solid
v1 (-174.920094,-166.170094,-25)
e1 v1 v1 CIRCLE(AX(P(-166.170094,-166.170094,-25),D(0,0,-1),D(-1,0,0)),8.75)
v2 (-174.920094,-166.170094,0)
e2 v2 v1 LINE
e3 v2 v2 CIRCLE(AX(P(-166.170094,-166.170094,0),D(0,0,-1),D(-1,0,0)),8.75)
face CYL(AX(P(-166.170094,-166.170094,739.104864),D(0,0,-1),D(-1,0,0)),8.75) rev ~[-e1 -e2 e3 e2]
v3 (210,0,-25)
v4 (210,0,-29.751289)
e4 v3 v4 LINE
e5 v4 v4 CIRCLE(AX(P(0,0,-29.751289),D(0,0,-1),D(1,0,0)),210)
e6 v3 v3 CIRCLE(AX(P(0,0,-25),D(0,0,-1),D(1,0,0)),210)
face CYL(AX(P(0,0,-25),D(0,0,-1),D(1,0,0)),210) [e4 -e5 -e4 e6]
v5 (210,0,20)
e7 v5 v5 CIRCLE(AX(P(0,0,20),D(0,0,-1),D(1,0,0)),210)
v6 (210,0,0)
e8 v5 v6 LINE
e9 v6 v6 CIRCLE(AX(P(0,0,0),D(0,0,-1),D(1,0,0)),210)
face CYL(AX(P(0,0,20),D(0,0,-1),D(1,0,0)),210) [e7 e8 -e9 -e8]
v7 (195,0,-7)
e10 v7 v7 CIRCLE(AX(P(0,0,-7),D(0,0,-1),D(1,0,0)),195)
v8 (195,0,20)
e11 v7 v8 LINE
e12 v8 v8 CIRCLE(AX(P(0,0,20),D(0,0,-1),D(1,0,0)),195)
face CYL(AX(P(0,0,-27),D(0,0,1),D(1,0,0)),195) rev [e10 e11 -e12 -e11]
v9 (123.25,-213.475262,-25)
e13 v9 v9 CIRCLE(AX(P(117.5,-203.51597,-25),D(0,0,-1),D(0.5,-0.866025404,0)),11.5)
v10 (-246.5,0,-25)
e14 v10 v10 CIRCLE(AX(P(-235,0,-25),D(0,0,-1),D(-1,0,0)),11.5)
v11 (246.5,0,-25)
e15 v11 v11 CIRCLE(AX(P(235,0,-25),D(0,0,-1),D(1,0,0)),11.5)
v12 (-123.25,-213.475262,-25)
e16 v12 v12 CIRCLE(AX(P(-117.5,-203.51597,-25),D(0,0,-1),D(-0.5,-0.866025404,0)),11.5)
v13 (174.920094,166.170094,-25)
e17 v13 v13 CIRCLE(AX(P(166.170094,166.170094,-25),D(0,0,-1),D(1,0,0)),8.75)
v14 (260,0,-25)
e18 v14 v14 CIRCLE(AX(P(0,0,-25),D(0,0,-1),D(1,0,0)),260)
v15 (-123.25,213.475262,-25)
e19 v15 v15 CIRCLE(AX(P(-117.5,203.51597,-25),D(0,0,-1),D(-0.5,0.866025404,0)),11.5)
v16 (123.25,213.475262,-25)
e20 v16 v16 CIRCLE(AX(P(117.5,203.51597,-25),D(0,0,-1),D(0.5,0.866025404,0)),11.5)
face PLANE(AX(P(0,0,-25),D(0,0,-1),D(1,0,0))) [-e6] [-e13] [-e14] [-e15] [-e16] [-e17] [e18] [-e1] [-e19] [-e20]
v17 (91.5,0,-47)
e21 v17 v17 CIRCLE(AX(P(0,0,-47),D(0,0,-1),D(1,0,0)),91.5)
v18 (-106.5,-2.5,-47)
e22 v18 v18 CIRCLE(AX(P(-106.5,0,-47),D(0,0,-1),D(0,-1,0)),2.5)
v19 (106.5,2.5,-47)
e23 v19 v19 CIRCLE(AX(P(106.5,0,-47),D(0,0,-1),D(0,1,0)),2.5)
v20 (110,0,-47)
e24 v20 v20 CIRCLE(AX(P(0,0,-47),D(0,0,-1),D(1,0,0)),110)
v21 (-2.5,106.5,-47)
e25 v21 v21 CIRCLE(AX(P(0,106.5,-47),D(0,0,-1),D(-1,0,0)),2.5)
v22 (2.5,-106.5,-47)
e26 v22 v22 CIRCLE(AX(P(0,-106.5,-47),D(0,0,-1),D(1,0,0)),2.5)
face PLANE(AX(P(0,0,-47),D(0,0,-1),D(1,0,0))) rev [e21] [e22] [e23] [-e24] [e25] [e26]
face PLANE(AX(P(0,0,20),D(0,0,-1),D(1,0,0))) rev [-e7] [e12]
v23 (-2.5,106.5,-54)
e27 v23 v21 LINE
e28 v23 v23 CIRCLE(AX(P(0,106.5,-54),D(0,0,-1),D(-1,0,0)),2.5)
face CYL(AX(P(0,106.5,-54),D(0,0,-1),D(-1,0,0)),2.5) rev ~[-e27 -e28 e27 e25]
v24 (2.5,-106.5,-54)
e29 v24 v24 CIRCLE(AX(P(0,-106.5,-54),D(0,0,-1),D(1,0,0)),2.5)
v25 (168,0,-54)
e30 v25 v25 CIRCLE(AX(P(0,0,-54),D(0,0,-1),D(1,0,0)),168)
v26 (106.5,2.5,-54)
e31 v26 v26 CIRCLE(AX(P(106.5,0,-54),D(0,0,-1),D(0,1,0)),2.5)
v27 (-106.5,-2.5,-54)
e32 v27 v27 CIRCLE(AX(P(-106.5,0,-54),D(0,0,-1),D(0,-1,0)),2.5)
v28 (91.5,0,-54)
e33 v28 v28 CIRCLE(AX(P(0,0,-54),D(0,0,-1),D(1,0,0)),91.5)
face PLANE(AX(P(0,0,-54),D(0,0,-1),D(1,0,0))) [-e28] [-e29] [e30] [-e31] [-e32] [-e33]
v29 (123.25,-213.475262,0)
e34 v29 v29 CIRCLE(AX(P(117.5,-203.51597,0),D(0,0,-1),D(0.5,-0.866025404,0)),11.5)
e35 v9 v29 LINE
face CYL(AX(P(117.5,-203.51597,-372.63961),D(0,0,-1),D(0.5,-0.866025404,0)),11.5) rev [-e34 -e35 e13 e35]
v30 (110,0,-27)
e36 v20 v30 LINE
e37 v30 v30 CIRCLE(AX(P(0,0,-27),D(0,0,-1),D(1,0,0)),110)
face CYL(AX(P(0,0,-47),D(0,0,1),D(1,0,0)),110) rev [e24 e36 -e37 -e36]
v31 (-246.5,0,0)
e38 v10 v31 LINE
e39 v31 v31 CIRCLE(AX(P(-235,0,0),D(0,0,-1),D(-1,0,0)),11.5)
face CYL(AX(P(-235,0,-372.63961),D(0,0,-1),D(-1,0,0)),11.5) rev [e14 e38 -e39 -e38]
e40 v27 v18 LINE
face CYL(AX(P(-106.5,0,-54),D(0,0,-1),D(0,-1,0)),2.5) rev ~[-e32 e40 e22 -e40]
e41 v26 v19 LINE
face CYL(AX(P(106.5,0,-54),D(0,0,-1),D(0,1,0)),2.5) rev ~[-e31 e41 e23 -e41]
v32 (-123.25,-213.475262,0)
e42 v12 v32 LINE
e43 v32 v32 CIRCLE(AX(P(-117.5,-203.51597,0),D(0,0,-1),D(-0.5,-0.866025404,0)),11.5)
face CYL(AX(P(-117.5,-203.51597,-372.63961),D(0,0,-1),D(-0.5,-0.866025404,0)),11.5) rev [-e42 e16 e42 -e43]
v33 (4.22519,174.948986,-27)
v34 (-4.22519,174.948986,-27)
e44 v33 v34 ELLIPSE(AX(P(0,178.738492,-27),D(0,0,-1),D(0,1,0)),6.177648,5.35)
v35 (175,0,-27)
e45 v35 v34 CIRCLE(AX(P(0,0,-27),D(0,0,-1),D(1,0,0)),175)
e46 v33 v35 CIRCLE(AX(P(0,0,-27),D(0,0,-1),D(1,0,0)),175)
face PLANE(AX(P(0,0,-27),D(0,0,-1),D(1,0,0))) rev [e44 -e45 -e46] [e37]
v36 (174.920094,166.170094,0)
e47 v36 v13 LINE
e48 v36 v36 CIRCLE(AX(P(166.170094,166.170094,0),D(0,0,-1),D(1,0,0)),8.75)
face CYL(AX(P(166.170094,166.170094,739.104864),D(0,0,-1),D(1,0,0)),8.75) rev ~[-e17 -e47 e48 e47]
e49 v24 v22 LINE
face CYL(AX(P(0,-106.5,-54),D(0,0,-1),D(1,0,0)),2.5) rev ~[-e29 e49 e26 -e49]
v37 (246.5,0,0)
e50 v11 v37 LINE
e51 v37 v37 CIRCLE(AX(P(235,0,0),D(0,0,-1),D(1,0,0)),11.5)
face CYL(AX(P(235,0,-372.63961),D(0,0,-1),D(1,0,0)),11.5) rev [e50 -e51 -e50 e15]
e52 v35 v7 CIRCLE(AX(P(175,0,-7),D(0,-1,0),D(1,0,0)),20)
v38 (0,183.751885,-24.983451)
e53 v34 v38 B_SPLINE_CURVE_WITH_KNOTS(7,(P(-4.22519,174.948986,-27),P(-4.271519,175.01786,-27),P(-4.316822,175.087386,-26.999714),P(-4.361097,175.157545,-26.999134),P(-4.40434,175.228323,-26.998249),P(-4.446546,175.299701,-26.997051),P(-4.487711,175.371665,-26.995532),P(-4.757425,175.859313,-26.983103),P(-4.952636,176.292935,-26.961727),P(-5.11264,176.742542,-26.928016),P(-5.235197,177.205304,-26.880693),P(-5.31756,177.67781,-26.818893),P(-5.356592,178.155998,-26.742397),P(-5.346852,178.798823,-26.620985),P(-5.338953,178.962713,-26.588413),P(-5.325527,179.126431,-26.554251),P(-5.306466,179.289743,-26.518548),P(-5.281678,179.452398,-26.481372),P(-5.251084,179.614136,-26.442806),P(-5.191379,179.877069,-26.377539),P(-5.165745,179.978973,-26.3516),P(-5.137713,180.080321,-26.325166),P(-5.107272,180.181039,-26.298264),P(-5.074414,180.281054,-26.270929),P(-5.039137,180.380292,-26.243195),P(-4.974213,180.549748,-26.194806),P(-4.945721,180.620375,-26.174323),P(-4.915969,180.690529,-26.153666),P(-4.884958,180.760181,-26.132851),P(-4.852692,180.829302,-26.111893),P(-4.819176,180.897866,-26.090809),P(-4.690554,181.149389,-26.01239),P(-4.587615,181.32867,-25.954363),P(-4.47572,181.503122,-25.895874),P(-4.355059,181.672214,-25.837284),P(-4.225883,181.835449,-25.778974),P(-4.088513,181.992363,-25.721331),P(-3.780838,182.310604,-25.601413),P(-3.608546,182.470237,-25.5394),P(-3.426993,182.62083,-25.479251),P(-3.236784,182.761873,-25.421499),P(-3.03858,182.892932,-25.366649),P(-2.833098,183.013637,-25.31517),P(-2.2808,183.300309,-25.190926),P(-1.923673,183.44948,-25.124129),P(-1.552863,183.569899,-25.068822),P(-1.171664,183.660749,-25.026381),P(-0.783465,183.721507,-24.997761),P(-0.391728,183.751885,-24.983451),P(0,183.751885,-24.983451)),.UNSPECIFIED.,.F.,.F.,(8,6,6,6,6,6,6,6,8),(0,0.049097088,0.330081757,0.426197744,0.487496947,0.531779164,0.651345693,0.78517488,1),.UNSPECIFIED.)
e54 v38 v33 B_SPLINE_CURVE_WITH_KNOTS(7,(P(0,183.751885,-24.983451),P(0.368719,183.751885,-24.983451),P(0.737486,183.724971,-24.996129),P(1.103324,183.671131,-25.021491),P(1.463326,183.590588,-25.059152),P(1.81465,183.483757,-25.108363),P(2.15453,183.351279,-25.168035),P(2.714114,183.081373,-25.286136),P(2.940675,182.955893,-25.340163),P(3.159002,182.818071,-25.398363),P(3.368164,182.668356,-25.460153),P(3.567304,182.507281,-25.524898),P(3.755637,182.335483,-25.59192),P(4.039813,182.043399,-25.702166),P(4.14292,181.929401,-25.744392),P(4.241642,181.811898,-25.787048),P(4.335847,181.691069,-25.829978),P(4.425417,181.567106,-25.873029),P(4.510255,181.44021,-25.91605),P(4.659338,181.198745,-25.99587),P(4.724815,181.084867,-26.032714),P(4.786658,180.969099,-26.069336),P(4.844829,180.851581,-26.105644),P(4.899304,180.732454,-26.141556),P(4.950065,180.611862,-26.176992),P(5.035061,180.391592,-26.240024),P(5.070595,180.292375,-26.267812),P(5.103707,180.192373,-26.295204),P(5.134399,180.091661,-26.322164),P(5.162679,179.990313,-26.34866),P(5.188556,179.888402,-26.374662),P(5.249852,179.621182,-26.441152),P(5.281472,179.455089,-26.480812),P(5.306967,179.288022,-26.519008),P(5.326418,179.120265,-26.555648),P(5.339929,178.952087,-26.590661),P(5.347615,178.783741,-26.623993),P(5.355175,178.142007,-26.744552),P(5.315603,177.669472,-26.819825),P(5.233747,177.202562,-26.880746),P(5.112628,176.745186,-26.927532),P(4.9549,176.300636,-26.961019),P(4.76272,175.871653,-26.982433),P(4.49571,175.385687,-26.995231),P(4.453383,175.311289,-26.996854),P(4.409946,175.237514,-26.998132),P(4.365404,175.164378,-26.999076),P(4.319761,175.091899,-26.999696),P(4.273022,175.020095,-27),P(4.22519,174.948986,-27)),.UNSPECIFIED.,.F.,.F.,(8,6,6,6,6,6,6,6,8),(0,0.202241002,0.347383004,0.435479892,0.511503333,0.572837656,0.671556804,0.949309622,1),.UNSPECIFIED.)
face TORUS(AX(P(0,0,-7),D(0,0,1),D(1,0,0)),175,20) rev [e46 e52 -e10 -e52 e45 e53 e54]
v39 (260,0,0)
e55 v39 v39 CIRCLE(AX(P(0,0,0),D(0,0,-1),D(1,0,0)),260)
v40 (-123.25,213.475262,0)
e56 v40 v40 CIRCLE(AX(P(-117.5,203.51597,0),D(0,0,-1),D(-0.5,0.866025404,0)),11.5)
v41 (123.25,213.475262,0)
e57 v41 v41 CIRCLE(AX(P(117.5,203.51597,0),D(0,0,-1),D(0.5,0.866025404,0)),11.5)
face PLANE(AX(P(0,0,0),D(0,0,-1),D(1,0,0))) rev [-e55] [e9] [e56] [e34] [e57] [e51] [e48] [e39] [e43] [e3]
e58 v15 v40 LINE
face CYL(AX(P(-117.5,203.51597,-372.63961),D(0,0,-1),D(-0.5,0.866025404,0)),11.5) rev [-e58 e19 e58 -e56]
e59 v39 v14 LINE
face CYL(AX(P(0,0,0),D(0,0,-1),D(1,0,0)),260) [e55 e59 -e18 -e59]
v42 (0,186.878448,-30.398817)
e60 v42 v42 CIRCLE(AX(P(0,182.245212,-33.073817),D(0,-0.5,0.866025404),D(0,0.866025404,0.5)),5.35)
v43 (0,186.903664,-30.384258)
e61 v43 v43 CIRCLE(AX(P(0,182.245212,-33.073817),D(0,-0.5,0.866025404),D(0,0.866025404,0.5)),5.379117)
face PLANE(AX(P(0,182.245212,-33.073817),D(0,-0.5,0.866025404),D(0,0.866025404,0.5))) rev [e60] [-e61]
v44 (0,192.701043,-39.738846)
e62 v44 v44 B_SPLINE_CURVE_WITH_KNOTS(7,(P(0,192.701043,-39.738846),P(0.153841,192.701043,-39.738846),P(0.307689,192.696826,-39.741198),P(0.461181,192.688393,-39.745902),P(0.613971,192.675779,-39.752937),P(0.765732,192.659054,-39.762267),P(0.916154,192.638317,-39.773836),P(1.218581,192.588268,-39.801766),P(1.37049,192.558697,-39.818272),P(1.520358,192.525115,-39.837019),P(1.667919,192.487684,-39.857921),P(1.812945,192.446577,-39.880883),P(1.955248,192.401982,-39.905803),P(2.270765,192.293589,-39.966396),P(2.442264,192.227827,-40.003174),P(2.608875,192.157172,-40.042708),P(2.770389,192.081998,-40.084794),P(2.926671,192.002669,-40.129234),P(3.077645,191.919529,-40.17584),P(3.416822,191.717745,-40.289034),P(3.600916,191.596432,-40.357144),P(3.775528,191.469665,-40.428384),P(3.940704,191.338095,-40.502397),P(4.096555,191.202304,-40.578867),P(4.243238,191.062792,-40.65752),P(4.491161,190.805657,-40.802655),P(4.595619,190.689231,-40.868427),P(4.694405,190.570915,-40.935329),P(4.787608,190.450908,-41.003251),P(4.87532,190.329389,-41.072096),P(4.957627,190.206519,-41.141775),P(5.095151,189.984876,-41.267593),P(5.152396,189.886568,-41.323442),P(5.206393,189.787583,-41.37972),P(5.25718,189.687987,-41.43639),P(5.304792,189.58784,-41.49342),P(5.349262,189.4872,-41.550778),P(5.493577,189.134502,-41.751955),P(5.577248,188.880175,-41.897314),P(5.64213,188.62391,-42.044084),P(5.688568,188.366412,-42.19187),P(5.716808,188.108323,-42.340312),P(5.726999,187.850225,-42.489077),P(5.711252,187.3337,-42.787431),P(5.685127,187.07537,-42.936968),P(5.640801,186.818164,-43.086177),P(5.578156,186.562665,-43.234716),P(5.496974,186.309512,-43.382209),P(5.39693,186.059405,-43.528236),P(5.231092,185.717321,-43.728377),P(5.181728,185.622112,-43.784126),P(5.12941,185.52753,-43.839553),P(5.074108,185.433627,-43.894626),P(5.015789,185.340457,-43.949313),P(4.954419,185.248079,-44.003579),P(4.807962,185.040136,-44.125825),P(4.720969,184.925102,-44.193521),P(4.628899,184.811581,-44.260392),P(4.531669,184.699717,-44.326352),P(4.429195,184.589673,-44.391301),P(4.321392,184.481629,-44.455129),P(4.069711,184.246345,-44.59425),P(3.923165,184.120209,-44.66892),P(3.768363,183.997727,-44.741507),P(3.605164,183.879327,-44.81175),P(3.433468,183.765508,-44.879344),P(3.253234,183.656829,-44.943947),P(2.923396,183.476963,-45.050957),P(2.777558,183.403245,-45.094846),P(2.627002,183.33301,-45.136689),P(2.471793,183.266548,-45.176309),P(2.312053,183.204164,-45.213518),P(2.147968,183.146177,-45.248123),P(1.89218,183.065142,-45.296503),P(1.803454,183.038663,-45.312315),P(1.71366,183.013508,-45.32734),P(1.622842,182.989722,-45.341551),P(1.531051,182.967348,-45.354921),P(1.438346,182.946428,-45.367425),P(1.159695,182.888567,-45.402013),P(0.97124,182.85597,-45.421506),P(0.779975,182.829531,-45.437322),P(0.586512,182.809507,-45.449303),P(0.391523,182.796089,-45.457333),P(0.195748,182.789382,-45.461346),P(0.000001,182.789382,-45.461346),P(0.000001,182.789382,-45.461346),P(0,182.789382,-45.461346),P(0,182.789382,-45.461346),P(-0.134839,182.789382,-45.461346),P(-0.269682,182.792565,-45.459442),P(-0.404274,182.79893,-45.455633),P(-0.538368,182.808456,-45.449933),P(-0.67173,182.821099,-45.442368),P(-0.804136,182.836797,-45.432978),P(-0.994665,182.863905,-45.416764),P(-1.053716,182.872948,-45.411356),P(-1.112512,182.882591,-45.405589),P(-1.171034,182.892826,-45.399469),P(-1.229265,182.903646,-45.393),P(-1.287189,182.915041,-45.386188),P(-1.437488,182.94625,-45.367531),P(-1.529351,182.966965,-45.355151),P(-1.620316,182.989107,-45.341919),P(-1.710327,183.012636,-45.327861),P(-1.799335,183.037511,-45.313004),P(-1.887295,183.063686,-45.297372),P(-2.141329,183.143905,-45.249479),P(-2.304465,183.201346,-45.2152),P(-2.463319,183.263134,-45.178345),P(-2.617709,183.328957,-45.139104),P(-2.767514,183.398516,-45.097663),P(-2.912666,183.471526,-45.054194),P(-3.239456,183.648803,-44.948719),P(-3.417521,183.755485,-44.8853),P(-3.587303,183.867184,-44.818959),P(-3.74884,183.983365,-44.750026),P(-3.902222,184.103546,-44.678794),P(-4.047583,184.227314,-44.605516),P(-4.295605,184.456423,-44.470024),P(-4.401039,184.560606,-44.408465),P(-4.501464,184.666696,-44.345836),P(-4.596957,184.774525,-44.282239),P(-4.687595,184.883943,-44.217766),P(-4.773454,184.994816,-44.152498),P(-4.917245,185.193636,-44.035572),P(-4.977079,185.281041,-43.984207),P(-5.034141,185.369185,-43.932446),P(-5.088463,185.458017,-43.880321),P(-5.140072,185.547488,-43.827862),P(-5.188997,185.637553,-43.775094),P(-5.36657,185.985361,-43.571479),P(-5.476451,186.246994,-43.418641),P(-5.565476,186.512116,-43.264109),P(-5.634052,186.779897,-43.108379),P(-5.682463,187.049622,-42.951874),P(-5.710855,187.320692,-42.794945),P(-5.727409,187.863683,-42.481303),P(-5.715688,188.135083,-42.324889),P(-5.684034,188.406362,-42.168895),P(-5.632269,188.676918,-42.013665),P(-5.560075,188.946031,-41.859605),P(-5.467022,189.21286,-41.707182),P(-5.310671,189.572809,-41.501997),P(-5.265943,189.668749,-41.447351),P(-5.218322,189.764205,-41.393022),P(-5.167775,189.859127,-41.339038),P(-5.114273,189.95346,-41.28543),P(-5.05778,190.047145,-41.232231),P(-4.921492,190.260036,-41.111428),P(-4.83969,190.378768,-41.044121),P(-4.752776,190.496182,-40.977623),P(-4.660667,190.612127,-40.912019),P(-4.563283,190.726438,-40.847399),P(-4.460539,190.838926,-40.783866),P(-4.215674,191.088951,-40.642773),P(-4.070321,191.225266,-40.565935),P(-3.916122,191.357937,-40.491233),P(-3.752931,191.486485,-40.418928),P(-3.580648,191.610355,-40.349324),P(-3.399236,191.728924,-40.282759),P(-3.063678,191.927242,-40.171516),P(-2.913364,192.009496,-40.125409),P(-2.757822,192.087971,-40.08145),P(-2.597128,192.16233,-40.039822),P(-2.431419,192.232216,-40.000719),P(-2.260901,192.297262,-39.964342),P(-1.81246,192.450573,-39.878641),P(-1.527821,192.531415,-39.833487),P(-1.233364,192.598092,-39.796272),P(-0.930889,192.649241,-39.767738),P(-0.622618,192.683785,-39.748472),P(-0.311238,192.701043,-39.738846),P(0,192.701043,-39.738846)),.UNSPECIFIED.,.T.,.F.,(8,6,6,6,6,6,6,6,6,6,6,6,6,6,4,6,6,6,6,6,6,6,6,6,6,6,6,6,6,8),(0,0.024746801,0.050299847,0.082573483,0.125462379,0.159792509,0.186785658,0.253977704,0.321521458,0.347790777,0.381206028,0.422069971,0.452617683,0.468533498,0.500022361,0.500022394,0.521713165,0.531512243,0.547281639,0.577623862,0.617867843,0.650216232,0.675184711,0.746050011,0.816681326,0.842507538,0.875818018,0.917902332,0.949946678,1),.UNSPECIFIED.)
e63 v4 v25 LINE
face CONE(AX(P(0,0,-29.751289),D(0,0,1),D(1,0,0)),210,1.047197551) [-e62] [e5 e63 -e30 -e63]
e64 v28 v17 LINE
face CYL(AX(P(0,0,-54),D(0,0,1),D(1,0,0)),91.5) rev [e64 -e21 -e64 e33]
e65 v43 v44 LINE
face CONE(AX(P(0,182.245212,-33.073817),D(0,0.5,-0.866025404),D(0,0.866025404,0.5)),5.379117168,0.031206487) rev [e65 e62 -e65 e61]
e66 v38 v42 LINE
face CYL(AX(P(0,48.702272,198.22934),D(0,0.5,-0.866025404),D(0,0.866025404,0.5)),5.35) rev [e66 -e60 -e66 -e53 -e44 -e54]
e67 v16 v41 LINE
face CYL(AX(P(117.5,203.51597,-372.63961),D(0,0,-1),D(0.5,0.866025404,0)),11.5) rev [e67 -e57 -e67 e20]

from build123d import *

# Parameters (mm, degrees)
FILLET1_R          = 20
CUT_EXTRUDE1_REACH = 377.068
SKETCH2_R          = 2.5
CIRPATTERN1_COUNT  = 4
CUT_EXTRUDE2_START = -372.639610375
SKETCH3_R          = 11.5
CUT_EXTRUDE2_DEPTH = 377.639610375
CIRPATTERN2_COUNT  = 6
M20_TAPPED_HOLE1_D = 17.5
CIRPATTERN3_COUNT  = 2


with BuildPart() as part:
    # Sketch1 → Revolve1 (revolve)
    with BuildSketch(Plane(origin=(0, 0, 0), x_dir=(0, 0, -1), z_dir=(1, 0, 0)), mode=Mode.PRIVATE) as revolve1_sk:
        Polygon((0, 260), (25, 260), (25, 210), (29.751288694, 210), (54, 168), (54, 91.5), (47, 91.5), (47, 110), (27, 110), (27, 195), (-20, 195), (-20, 210), (0, 210), align=None)
    revolve(revolve1_sk.sketch.rotate(Axis((0, 0, 141.233138436), (0, 0, -1)), 90), axis=Axis((0, 0, 141.233138436), (0, 0, -1)))

    # Fillet1
    fillet1_edges = [part.edges().sort_by_distance(p)[0] for p in [
        (-195, 0, -27),
    ]]
    fillet(fillet1_edges, radius=FILLET1_R)

    # Sketch2 → Cut-Extrude1 (cut, up to next)
    with BuildSketch(Plane(origin=(0, 0, -54), x_dir=(-1, 0, 0), z_dir=(0, 0, -1)), mode=Mode.PRIVATE) as cut_extrude1_sk1:
        with Locations((0, 106.5)):
            Circle(SKETCH2_R)
    cut_extrude1_tool1 = extrude(cut_extrude1_sk1.sketch, amount=-CUT_EXTRUDE1_REACH, mode=Mode.PRIVATE) & part.part
    cut_extrude1 = cut_extrude1_tool1.solids().sort_by_distance((0, 106.5, -54))[0]
    add(cut_extrude1, mode=Mode.SUBTRACT)

    # CirPattern1: Cut-Extrude1 ×4 about axis
    cirpattern1_axis = Axis((0, 0, 0), (0, 0, 1))
    for i in range(1, CIRPATTERN1_COUNT):
        add(cut_extrude1.rotate(cirpattern1_axis, i * 360 / CIRPATTERN1_COUNT), mode=Mode.SUBTRACT)

    # Sketch3 → Cut-Extrude2 (cut)
    with BuildSketch(Plane.XY.offset(CUT_EXTRUDE2_START)):
        with Locations(Location((-235, 0, 0), (0, 0, 180))):
            Circle(SKETCH3_R)
    cut_extrude2 = extrude(amount=CUT_EXTRUDE2_DEPTH, mode=Mode.SUBTRACT)

    # CirPattern2: Cut-Extrude2 ×6 about axis
    cirpattern2_axis = Axis((0, 0, 0), (0, 0, 1))
    for i in range(1, CIRPATTERN2_COUNT):
        add(cut_extrude2.rotate(cirpattern2_axis, i * 360 / CIRPATTERN2_COUNT), mode=Mode.SUBTRACT)

    # M20 Tapped Hole1 (through all)
    with Locations(Plane.XY):
        with Locations((-166.170093579, -166.170093579)):
            m20_tapped_hole1 = Hole(M20_TAPPED_HOLE1_D / 2)

    # CirPattern3: M20 Tapped Hole1 ×2 about axis
    cirpattern3_axis = Axis((0, 0, 0), (0, 0, 1))
    for i in range(1, CIRPATTERN3_COUNT):
        add(m20_tapped_hole1.rotate(cirpattern3_axis, i * 360 / CIRPATTERN3_COUNT), mode=Mode.SUBTRACT)

    # Sketch6 → 1/4 Rc Tapped Hole1 (revolve, cut)
    with BuildSketch(Plane(origin=(0, 187.745212251, -42.600096392), x_dir=(0, 0.8660254037844378, 0.5000000000000014), z_dir=(1, 0, 0))):
        Polygon((0, 0), (0, 278.08587988), (5.35, 278.08587988), (5.35, 11), (5.379117168, 11), (5.7225, 0), align=None)
    revolve(axis=Axis((0, 190.920212251, -48.099357706), (-1.8069730093789398e-15, -0.5000000000000014, 0.8660254037844378)), mode=Mode.SUBTRACT)


solid = part.part
